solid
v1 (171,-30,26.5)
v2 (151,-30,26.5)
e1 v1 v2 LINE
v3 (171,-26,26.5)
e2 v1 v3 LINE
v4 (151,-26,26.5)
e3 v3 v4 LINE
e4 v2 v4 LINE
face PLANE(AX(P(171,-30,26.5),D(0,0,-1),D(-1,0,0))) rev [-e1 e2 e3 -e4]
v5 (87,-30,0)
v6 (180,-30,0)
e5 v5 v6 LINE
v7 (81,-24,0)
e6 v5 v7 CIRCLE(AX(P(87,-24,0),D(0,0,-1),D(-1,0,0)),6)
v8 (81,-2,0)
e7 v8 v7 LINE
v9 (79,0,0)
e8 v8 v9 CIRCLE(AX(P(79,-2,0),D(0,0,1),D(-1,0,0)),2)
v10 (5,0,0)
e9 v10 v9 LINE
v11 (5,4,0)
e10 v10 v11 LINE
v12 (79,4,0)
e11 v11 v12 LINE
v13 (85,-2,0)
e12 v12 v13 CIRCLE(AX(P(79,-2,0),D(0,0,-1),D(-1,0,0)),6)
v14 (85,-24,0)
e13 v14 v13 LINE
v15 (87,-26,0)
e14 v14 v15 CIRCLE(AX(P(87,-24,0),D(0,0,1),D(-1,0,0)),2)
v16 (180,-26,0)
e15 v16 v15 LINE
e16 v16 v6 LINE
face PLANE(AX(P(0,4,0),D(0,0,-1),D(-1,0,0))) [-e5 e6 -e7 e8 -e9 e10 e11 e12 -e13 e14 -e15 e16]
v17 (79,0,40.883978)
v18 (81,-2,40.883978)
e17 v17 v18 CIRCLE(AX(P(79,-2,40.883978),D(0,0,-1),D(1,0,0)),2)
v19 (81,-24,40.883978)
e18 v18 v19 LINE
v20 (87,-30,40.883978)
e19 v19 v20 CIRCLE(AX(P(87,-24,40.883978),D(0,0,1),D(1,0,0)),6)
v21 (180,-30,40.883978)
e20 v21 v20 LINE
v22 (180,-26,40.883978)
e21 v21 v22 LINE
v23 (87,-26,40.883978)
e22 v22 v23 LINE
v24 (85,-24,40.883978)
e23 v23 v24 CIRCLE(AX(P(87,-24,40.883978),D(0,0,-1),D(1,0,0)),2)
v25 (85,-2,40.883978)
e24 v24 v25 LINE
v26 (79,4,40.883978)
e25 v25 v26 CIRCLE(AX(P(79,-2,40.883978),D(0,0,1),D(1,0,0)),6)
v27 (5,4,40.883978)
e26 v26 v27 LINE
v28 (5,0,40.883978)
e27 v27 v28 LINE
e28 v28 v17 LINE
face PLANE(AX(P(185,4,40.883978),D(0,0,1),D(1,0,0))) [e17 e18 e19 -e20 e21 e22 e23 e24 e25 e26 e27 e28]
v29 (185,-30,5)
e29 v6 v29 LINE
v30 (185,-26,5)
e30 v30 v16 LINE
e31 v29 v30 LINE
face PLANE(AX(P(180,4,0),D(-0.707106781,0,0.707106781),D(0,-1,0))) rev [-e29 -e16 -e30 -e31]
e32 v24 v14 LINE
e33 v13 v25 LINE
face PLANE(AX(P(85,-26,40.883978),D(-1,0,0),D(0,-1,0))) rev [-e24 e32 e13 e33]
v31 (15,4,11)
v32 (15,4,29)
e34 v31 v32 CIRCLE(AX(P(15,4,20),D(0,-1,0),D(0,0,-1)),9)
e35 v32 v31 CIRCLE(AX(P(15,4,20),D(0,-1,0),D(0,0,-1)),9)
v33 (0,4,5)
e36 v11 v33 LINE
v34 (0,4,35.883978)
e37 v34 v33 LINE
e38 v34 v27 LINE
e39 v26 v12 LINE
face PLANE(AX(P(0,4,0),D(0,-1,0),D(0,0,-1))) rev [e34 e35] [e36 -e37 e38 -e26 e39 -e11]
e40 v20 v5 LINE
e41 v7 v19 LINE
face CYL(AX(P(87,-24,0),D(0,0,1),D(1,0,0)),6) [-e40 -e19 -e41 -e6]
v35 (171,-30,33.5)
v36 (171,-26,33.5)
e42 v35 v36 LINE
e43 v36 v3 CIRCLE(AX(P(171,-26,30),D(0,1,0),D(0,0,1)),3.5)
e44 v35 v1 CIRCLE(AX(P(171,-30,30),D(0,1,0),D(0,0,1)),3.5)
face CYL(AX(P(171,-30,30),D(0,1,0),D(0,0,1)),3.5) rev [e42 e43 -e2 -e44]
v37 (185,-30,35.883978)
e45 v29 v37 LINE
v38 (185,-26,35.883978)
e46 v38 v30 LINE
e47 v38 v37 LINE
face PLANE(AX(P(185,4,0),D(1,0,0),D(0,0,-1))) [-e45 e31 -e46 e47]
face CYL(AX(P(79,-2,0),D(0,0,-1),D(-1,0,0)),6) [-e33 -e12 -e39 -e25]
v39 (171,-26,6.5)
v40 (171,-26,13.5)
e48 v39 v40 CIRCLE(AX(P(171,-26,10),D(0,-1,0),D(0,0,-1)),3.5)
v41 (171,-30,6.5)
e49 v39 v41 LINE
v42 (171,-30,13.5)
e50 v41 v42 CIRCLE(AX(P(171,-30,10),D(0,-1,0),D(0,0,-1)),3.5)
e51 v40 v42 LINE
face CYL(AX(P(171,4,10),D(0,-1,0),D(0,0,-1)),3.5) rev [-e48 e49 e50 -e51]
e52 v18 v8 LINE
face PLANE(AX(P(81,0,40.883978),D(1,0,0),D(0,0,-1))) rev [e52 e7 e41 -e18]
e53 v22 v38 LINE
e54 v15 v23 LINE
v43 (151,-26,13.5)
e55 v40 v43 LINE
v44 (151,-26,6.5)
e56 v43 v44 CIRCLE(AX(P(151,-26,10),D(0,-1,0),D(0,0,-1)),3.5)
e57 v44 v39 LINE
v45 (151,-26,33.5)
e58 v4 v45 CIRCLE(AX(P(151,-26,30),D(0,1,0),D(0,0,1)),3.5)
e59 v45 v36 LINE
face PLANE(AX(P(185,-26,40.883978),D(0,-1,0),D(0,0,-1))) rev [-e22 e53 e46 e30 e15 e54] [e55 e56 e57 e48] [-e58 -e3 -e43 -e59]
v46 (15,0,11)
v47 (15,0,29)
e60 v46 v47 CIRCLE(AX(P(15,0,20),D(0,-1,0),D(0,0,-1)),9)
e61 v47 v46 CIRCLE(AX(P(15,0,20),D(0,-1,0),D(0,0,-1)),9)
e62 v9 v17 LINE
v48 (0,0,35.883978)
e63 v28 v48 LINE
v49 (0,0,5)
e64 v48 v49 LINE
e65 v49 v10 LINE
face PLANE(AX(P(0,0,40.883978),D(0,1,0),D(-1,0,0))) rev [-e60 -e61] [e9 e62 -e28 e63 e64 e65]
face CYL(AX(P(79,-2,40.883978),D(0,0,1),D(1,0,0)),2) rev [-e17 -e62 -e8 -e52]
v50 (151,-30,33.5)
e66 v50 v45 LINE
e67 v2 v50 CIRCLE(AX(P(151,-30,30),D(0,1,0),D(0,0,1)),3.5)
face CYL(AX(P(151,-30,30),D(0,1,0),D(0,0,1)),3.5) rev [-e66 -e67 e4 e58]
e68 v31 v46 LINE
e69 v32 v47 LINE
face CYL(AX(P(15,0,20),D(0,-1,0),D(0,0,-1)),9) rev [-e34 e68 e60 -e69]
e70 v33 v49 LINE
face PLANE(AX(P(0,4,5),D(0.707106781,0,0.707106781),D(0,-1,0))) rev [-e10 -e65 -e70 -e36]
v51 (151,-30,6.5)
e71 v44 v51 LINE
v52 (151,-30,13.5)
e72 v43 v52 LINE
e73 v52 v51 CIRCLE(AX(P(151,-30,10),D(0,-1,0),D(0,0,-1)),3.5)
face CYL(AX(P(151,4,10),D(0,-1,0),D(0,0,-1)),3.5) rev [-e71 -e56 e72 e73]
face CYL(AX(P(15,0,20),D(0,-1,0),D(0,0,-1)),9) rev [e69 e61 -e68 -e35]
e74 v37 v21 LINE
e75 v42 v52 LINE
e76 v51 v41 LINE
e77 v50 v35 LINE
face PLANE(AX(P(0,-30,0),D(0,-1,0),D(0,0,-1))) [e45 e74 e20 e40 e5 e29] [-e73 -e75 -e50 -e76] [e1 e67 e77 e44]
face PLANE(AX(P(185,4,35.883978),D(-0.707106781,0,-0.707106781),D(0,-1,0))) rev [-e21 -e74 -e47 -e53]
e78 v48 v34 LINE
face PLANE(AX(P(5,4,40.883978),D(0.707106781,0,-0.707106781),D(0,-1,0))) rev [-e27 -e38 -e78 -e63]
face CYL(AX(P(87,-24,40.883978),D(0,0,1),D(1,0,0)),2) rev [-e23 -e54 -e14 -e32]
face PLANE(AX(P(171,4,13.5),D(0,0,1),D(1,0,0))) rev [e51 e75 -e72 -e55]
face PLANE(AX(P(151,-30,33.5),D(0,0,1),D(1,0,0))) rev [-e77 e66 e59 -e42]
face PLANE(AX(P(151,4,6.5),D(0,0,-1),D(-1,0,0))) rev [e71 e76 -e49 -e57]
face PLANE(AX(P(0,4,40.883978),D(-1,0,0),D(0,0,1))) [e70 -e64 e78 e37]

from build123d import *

# Parameters (mm, degrees)
SKETCH_1_W              = 185
SKETCH_1_H              = 40.883977901
EXTRUDE_1_DEPTH         = 34
SKETCH_2_W              = 100
SKETCH_2_H              = 30
CUT_EXTRUDE_1_DEPTH     = 192.824137295
SKETCH_3_W              = 81
SKETCH_3_H              = 30
CUT_EXTRUDE_2_DEPTH     = 192.824137295
CUT_EXTRUDE_3_DEPTH     = 193.490258582
CUT_EXTRUDE_4_DEPTH     = 192.824137295
HOLE_WIZARD_18_0_18_1_D = 18
CHAMFER_1_SIZE          = 5
FILLET_1_R              = 2
FILLET_2_R              = 6


with BuildPart() as part:
    # 草图1 → 凸台-拉伸1 (new body)
    with BuildSketch(Plane.XZ.offset(30)):
        with Locations((92.5, 20.441988951)):
            Rectangle(SKETCH_1_W, SKETCH_1_H)
    extrude(amount=-EXTRUDE_1_DEPTH)

    # 草图2 → 切除-拉伸1 (cut, through all)
    with BuildSketch(Plane(origin=(0, 0, 0), x_dir=(-1, 0, 0), z_dir=(0, 0, -1))):
        with Locations((-135, -11)):
            Rectangle(SKETCH_2_W, SKETCH_2_H)
    extrude(amount=-CUT_EXTRUDE_1_DEPTH, mode=Mode.SUBTRACT)

    # 草图3 → 切除-拉伸2 (cut, through all)
    with BuildSketch(Plane(origin=(0, 0, 0), x_dir=(-1, 0, 0), z_dir=(0, 0, -1))):
        with Locations((-40.5, -15)):
            Rectangle(SKETCH_3_W, SKETCH_3_H)
    extrude(amount=-CUT_EXTRUDE_2_DEPTH, mode=Mode.SUBTRACT)

    # 草图4 → 切除-拉伸3 (cut, through all)
    with BuildSketch(Plane.XZ.offset(30)):
        with BuildLine():
            Line((171, 13.5), (151, 13.5))
            ThreePointArc((151, 13.5), (147.5, 10), (151, 6.5))
            Line((151, 6.5), (171, 6.5))
            ThreePointArc((171, 6.5), (174.5, 10), (171, 13.5))
        make_face()
    extrude(amount=-CUT_EXTRUDE_3_DEPTH, mode=Mode.SUBTRACT)

    # 草图5 → 切除-拉伸4 (cut, through all)
    with BuildSketch(Plane(origin=(0, -26, 0), x_dir=(-1, 0, 0), z_dir=(0, 1, 0))):
        with BuildLine():
            Line((-151, 33.5), (-171, 33.5))
            ThreePointArc((-171, 33.5), (-174.5, 30), (-171, 26.5))
            Line((-171, 26.5), (-151, 26.5))
            ThreePointArc((-151, 26.5), (-147.5, 30), (-151, 33.5))
        make_face()
    extrude(amount=-CUT_EXTRUDE_4_DEPTH, mode=Mode.SUBTRACT)

    # Ø18.0 (18) 直径孔1 (through all)
    with Locations(Plane(origin=(0, 0, 0), x_dir=(-1, 0, 0), z_dir=(0, -1, 0))):
        with Locations((-15, -20)):
            Hole(HOLE_WIZARD_18_0_18_1_D / 2)

    # 倒角1
    chamfer_1_edges = [part.edges().sort_by_distance(p)[0] for p in [
        (185, -28, 0),
        (185, -28, 40.883977901),
        (0, 2, 40.883977901),
        (0, 2, 0),
    ]]
    chamfer(chamfer_1_edges, length=CHAMFER_1_SIZE)

    # 圆角1
    fillet_1_edges = [part.edges().sort_by_distance(p)[0] for p in [
        (85, -26, 20.44198895),
        (81, 0, 20.44198895),
    ]]
    fillet(fillet_1_edges, radius=FILLET_1_R)

    # 圆角2
    fillet_2_edges = [part.edges().sort_by_distance(p)[0] for p in [
        (85, 4, 20.44198895),
        (81, -30, 20.44198895),
    ]]
    fillet(fillet_2_edges, radius=FILLET_2_R)


solid = part.part
